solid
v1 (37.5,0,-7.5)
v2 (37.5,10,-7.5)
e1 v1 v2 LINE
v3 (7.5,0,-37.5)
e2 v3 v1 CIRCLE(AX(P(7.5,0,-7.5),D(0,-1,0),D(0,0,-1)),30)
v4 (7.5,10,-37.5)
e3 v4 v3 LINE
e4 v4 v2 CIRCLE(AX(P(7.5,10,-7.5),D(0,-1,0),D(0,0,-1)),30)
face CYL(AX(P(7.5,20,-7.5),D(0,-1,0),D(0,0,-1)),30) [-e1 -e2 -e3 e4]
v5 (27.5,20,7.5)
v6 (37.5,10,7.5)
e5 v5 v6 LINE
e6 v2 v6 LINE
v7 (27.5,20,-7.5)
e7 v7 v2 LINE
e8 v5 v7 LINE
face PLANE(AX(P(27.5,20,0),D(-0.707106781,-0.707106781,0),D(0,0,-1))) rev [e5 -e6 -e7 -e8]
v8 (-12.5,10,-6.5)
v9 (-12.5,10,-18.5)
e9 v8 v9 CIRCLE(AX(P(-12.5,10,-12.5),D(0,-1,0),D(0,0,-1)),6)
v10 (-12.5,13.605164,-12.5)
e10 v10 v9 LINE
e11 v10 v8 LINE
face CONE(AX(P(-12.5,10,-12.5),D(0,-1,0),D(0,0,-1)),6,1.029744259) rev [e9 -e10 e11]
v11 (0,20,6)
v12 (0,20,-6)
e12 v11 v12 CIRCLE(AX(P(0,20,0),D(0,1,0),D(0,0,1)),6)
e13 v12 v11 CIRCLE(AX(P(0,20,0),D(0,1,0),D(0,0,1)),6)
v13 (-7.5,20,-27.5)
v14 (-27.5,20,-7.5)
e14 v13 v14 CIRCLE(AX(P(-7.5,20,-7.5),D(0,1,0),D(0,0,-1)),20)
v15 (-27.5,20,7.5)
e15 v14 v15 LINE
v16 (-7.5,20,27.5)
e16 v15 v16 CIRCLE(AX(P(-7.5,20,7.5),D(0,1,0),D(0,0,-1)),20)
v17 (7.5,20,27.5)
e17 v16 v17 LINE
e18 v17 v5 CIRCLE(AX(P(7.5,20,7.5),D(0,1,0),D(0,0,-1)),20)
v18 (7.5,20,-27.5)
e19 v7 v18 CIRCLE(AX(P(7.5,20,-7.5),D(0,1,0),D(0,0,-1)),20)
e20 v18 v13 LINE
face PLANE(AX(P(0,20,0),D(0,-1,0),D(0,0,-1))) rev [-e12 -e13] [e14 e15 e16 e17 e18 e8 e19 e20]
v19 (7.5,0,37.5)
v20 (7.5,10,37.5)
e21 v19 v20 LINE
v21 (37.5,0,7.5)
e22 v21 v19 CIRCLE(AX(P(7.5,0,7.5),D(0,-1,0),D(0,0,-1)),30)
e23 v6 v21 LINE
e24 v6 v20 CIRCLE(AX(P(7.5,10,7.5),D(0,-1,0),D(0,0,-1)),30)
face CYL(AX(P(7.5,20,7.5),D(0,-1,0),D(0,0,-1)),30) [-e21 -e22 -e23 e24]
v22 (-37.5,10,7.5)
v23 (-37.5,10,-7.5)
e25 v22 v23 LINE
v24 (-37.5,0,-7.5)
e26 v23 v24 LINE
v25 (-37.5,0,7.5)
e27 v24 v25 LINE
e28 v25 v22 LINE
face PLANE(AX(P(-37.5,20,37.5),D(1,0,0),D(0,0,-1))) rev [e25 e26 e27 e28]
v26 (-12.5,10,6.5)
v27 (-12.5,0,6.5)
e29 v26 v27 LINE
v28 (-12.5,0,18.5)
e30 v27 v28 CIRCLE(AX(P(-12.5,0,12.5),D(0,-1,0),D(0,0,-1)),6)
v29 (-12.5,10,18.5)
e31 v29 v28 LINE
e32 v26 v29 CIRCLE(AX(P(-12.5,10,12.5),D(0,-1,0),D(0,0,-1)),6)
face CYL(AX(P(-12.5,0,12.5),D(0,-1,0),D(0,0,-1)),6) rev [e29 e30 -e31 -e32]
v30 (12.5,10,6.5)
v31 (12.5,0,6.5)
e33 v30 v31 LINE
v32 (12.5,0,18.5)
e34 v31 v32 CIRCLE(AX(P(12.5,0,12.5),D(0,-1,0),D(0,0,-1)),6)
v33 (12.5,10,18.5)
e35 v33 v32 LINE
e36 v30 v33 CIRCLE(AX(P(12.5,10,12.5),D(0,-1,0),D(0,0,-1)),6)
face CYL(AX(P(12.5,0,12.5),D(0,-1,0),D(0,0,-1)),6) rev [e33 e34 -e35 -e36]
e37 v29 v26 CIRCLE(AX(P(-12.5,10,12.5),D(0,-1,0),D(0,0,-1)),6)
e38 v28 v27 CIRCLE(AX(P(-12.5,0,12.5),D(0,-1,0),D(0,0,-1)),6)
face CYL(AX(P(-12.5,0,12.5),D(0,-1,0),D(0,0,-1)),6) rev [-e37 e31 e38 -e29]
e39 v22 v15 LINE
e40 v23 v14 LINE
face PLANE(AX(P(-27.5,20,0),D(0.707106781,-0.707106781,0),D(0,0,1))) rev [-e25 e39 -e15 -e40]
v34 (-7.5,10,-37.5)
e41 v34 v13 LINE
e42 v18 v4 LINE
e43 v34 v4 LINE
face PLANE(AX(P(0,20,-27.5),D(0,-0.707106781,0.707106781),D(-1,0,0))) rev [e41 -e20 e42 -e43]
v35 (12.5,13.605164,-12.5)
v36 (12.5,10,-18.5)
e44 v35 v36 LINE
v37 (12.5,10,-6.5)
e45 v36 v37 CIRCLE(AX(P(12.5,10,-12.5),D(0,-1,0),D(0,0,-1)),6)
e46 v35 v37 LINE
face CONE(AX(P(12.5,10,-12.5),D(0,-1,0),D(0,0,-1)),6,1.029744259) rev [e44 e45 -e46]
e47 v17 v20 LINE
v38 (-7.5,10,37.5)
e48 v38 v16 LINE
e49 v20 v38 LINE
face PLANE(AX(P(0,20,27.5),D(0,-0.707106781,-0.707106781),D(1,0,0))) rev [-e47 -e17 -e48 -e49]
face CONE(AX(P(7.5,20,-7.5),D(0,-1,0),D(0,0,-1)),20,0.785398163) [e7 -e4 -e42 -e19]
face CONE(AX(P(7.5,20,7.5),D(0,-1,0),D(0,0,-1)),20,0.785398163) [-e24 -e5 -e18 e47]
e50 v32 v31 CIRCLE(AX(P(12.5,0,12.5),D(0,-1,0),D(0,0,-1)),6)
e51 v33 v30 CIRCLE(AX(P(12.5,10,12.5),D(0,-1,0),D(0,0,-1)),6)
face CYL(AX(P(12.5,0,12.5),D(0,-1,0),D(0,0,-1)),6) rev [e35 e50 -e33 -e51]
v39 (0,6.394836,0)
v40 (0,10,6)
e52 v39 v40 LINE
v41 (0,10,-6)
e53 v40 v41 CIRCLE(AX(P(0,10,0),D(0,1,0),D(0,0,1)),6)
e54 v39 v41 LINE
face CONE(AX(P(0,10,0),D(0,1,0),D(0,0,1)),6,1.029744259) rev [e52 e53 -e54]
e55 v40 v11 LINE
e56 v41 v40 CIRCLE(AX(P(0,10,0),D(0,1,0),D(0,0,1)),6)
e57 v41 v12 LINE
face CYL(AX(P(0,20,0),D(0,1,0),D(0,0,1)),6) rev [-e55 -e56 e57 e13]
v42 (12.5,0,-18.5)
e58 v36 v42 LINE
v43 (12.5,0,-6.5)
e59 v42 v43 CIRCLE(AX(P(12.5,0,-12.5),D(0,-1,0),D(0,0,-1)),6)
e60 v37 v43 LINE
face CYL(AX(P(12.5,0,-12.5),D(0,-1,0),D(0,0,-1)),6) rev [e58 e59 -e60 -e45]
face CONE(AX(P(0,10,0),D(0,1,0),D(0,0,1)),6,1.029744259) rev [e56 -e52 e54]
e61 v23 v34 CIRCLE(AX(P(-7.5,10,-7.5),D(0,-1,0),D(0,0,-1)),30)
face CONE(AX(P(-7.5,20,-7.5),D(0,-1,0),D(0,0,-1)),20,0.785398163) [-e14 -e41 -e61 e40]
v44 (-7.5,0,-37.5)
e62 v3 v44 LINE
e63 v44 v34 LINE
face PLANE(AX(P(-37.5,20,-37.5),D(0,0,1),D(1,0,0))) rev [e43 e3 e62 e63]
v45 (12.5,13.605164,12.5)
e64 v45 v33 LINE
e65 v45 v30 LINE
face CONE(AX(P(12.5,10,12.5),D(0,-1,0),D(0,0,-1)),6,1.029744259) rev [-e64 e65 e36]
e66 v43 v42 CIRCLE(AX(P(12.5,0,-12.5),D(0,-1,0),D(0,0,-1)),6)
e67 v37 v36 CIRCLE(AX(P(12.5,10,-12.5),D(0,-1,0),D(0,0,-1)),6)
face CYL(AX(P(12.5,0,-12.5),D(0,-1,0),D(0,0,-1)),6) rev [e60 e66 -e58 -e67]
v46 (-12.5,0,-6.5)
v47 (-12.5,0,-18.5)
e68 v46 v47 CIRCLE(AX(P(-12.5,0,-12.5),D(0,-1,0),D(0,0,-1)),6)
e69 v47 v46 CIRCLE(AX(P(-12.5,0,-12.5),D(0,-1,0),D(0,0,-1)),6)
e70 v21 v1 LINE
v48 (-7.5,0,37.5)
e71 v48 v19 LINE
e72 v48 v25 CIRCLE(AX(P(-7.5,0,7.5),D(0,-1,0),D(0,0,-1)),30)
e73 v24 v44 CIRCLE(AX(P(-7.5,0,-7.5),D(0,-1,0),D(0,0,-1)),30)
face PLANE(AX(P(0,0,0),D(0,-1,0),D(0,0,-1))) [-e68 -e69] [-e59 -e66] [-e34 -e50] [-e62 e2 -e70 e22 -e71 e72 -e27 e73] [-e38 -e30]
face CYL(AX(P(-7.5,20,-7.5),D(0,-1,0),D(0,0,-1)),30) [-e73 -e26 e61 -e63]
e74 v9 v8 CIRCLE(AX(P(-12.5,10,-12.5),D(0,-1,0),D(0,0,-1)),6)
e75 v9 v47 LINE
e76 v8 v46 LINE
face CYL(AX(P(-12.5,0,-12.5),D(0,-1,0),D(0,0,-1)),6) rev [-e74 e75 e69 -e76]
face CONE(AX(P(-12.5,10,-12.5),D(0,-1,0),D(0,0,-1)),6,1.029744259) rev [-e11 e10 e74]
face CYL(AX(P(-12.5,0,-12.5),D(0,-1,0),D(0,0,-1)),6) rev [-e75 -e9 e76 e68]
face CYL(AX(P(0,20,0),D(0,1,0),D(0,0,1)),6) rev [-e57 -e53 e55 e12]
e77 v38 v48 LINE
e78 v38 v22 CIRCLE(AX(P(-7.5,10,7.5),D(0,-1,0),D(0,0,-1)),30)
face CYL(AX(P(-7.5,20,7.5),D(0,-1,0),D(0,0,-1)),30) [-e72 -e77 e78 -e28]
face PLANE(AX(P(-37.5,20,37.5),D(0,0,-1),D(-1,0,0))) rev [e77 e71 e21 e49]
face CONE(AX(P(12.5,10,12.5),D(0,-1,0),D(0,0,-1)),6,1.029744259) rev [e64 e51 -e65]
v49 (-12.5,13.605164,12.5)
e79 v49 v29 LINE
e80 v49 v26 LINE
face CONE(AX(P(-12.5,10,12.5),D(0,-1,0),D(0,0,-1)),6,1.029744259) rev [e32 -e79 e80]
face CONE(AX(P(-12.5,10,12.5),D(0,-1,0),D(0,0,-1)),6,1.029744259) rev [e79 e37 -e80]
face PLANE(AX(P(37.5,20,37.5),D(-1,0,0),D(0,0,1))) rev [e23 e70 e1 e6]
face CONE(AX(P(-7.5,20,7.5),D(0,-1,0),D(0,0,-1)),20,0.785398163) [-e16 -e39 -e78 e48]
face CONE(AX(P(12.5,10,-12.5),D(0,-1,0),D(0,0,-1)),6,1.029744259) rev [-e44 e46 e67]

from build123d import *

# Parameters (mm, degrees)
BASE_PROFILE_SKETCH_75X75_W    = 75
BASE_PROFILE_SKETCH_75X75_H    = 75
BASE_BLOCK_75X75X20_DEPTH      = 20
CORNER_FILLETS_R30_R           = 30
TOP_EDGE_CHAMFER_10X45DEG_SIZE = 10
DOWEL_HOLE_A_12X10_D           = 12
DOWEL_HOLE_A_12X10_DEPTH       = 10
DOWEL_HOLE_A_12X10_TIP         = 3.605163714
DOWEL_HOLE_B_12X10_D           = 12
DOWEL_HOLE_B_12X10_DEPTH       = 10
DOWEL_HOLE_B_12X10_TIP         = 3.605163714


with BuildPart() as part:
    # Base Profile Sketch 75x75 → Base Block 75x75x20 (new body)
    with BuildSketch(Plane(origin=(0, 0, 0), x_dir=(1, 0, 0), z_dir=(0, 1, 0))):
        Rectangle(BASE_PROFILE_SKETCH_75X75_W, BASE_PROFILE_SKETCH_75X75_H)
    extrude(amount=BASE_BLOCK_75X75X20_DEPTH)

    # Corner Fillets R30
    corner_fillets_r30_edges = [part.edges().sort_by_distance(p)[0] for p in [
        (37.5, 10, 37.5),
        (-37.5, 10, 37.5),
        (-37.5, 10, -37.5),
        (37.5, 10, -37.5),
    ]]
    fillet(corner_fillets_r30_edges, radius=CORNER_FILLETS_R30_R)

    # Top Edge Chamfer 10x45deg
    top_edge_chamfer_10x45deg_edges = [part.edges().sort_by_distance(p)[0] for p in [
        (-37.5, 20, 0),
        (0, 20, -37.5),
        (37.5, 20, 0),
        (0, 20, 37.5),
        (-28.713203436, 20, 28.713203436),
        (28.713203436, 20, 28.713203436),
        (28.713203436, 20, -28.713203436),
        (-28.713203436, 20, -28.713203436),
    ]]
    chamfer(top_edge_chamfer_10x45deg_edges, length=TOP_EDGE_CHAMFER_10X45DEG_SIZE)

    # Dowel Hole A Ø12x10
    with Locations(Plane.ZX.offset(20)):
        with Locations((0, 0)):
            Hole(DOWEL_HOLE_A_12X10_D / 2, depth=DOWEL_HOLE_A_12X10_DEPTH)
            with Locations((0, 0, -(DOWEL_HOLE_A_12X10_DEPTH + DOWEL_HOLE_A_12X10_TIP / 2))):  # 118° drill point
                Cone(0, DOWEL_HOLE_A_12X10_D / 2, DOWEL_HOLE_A_12X10_TIP, mode=Mode.SUBTRACT)

    # Dowel Hole B Ø12x10
    with Locations(Plane(origin=(-12.5, 0, 12.5), x_dir=(0, 0, -1), z_dir=(0, -1, 0))):
        with Locations((0, 0), (0, 25), (25, 25), (25, 0)):
            Hole(DOWEL_HOLE_B_12X10_D / 2, depth=DOWEL_HOLE_B_12X10_DEPTH)
            with Locations((0, 0, -(DOWEL_HOLE_B_12X10_DEPTH + DOWEL_HOLE_B_12X10_TIP / 2))):  # 118° drill point
                Cone(0, DOWEL_HOLE_B_12X10_D / 2, DOWEL_HOLE_B_12X10_TIP, mode=Mode.SUBTRACT)


solid = part.part
